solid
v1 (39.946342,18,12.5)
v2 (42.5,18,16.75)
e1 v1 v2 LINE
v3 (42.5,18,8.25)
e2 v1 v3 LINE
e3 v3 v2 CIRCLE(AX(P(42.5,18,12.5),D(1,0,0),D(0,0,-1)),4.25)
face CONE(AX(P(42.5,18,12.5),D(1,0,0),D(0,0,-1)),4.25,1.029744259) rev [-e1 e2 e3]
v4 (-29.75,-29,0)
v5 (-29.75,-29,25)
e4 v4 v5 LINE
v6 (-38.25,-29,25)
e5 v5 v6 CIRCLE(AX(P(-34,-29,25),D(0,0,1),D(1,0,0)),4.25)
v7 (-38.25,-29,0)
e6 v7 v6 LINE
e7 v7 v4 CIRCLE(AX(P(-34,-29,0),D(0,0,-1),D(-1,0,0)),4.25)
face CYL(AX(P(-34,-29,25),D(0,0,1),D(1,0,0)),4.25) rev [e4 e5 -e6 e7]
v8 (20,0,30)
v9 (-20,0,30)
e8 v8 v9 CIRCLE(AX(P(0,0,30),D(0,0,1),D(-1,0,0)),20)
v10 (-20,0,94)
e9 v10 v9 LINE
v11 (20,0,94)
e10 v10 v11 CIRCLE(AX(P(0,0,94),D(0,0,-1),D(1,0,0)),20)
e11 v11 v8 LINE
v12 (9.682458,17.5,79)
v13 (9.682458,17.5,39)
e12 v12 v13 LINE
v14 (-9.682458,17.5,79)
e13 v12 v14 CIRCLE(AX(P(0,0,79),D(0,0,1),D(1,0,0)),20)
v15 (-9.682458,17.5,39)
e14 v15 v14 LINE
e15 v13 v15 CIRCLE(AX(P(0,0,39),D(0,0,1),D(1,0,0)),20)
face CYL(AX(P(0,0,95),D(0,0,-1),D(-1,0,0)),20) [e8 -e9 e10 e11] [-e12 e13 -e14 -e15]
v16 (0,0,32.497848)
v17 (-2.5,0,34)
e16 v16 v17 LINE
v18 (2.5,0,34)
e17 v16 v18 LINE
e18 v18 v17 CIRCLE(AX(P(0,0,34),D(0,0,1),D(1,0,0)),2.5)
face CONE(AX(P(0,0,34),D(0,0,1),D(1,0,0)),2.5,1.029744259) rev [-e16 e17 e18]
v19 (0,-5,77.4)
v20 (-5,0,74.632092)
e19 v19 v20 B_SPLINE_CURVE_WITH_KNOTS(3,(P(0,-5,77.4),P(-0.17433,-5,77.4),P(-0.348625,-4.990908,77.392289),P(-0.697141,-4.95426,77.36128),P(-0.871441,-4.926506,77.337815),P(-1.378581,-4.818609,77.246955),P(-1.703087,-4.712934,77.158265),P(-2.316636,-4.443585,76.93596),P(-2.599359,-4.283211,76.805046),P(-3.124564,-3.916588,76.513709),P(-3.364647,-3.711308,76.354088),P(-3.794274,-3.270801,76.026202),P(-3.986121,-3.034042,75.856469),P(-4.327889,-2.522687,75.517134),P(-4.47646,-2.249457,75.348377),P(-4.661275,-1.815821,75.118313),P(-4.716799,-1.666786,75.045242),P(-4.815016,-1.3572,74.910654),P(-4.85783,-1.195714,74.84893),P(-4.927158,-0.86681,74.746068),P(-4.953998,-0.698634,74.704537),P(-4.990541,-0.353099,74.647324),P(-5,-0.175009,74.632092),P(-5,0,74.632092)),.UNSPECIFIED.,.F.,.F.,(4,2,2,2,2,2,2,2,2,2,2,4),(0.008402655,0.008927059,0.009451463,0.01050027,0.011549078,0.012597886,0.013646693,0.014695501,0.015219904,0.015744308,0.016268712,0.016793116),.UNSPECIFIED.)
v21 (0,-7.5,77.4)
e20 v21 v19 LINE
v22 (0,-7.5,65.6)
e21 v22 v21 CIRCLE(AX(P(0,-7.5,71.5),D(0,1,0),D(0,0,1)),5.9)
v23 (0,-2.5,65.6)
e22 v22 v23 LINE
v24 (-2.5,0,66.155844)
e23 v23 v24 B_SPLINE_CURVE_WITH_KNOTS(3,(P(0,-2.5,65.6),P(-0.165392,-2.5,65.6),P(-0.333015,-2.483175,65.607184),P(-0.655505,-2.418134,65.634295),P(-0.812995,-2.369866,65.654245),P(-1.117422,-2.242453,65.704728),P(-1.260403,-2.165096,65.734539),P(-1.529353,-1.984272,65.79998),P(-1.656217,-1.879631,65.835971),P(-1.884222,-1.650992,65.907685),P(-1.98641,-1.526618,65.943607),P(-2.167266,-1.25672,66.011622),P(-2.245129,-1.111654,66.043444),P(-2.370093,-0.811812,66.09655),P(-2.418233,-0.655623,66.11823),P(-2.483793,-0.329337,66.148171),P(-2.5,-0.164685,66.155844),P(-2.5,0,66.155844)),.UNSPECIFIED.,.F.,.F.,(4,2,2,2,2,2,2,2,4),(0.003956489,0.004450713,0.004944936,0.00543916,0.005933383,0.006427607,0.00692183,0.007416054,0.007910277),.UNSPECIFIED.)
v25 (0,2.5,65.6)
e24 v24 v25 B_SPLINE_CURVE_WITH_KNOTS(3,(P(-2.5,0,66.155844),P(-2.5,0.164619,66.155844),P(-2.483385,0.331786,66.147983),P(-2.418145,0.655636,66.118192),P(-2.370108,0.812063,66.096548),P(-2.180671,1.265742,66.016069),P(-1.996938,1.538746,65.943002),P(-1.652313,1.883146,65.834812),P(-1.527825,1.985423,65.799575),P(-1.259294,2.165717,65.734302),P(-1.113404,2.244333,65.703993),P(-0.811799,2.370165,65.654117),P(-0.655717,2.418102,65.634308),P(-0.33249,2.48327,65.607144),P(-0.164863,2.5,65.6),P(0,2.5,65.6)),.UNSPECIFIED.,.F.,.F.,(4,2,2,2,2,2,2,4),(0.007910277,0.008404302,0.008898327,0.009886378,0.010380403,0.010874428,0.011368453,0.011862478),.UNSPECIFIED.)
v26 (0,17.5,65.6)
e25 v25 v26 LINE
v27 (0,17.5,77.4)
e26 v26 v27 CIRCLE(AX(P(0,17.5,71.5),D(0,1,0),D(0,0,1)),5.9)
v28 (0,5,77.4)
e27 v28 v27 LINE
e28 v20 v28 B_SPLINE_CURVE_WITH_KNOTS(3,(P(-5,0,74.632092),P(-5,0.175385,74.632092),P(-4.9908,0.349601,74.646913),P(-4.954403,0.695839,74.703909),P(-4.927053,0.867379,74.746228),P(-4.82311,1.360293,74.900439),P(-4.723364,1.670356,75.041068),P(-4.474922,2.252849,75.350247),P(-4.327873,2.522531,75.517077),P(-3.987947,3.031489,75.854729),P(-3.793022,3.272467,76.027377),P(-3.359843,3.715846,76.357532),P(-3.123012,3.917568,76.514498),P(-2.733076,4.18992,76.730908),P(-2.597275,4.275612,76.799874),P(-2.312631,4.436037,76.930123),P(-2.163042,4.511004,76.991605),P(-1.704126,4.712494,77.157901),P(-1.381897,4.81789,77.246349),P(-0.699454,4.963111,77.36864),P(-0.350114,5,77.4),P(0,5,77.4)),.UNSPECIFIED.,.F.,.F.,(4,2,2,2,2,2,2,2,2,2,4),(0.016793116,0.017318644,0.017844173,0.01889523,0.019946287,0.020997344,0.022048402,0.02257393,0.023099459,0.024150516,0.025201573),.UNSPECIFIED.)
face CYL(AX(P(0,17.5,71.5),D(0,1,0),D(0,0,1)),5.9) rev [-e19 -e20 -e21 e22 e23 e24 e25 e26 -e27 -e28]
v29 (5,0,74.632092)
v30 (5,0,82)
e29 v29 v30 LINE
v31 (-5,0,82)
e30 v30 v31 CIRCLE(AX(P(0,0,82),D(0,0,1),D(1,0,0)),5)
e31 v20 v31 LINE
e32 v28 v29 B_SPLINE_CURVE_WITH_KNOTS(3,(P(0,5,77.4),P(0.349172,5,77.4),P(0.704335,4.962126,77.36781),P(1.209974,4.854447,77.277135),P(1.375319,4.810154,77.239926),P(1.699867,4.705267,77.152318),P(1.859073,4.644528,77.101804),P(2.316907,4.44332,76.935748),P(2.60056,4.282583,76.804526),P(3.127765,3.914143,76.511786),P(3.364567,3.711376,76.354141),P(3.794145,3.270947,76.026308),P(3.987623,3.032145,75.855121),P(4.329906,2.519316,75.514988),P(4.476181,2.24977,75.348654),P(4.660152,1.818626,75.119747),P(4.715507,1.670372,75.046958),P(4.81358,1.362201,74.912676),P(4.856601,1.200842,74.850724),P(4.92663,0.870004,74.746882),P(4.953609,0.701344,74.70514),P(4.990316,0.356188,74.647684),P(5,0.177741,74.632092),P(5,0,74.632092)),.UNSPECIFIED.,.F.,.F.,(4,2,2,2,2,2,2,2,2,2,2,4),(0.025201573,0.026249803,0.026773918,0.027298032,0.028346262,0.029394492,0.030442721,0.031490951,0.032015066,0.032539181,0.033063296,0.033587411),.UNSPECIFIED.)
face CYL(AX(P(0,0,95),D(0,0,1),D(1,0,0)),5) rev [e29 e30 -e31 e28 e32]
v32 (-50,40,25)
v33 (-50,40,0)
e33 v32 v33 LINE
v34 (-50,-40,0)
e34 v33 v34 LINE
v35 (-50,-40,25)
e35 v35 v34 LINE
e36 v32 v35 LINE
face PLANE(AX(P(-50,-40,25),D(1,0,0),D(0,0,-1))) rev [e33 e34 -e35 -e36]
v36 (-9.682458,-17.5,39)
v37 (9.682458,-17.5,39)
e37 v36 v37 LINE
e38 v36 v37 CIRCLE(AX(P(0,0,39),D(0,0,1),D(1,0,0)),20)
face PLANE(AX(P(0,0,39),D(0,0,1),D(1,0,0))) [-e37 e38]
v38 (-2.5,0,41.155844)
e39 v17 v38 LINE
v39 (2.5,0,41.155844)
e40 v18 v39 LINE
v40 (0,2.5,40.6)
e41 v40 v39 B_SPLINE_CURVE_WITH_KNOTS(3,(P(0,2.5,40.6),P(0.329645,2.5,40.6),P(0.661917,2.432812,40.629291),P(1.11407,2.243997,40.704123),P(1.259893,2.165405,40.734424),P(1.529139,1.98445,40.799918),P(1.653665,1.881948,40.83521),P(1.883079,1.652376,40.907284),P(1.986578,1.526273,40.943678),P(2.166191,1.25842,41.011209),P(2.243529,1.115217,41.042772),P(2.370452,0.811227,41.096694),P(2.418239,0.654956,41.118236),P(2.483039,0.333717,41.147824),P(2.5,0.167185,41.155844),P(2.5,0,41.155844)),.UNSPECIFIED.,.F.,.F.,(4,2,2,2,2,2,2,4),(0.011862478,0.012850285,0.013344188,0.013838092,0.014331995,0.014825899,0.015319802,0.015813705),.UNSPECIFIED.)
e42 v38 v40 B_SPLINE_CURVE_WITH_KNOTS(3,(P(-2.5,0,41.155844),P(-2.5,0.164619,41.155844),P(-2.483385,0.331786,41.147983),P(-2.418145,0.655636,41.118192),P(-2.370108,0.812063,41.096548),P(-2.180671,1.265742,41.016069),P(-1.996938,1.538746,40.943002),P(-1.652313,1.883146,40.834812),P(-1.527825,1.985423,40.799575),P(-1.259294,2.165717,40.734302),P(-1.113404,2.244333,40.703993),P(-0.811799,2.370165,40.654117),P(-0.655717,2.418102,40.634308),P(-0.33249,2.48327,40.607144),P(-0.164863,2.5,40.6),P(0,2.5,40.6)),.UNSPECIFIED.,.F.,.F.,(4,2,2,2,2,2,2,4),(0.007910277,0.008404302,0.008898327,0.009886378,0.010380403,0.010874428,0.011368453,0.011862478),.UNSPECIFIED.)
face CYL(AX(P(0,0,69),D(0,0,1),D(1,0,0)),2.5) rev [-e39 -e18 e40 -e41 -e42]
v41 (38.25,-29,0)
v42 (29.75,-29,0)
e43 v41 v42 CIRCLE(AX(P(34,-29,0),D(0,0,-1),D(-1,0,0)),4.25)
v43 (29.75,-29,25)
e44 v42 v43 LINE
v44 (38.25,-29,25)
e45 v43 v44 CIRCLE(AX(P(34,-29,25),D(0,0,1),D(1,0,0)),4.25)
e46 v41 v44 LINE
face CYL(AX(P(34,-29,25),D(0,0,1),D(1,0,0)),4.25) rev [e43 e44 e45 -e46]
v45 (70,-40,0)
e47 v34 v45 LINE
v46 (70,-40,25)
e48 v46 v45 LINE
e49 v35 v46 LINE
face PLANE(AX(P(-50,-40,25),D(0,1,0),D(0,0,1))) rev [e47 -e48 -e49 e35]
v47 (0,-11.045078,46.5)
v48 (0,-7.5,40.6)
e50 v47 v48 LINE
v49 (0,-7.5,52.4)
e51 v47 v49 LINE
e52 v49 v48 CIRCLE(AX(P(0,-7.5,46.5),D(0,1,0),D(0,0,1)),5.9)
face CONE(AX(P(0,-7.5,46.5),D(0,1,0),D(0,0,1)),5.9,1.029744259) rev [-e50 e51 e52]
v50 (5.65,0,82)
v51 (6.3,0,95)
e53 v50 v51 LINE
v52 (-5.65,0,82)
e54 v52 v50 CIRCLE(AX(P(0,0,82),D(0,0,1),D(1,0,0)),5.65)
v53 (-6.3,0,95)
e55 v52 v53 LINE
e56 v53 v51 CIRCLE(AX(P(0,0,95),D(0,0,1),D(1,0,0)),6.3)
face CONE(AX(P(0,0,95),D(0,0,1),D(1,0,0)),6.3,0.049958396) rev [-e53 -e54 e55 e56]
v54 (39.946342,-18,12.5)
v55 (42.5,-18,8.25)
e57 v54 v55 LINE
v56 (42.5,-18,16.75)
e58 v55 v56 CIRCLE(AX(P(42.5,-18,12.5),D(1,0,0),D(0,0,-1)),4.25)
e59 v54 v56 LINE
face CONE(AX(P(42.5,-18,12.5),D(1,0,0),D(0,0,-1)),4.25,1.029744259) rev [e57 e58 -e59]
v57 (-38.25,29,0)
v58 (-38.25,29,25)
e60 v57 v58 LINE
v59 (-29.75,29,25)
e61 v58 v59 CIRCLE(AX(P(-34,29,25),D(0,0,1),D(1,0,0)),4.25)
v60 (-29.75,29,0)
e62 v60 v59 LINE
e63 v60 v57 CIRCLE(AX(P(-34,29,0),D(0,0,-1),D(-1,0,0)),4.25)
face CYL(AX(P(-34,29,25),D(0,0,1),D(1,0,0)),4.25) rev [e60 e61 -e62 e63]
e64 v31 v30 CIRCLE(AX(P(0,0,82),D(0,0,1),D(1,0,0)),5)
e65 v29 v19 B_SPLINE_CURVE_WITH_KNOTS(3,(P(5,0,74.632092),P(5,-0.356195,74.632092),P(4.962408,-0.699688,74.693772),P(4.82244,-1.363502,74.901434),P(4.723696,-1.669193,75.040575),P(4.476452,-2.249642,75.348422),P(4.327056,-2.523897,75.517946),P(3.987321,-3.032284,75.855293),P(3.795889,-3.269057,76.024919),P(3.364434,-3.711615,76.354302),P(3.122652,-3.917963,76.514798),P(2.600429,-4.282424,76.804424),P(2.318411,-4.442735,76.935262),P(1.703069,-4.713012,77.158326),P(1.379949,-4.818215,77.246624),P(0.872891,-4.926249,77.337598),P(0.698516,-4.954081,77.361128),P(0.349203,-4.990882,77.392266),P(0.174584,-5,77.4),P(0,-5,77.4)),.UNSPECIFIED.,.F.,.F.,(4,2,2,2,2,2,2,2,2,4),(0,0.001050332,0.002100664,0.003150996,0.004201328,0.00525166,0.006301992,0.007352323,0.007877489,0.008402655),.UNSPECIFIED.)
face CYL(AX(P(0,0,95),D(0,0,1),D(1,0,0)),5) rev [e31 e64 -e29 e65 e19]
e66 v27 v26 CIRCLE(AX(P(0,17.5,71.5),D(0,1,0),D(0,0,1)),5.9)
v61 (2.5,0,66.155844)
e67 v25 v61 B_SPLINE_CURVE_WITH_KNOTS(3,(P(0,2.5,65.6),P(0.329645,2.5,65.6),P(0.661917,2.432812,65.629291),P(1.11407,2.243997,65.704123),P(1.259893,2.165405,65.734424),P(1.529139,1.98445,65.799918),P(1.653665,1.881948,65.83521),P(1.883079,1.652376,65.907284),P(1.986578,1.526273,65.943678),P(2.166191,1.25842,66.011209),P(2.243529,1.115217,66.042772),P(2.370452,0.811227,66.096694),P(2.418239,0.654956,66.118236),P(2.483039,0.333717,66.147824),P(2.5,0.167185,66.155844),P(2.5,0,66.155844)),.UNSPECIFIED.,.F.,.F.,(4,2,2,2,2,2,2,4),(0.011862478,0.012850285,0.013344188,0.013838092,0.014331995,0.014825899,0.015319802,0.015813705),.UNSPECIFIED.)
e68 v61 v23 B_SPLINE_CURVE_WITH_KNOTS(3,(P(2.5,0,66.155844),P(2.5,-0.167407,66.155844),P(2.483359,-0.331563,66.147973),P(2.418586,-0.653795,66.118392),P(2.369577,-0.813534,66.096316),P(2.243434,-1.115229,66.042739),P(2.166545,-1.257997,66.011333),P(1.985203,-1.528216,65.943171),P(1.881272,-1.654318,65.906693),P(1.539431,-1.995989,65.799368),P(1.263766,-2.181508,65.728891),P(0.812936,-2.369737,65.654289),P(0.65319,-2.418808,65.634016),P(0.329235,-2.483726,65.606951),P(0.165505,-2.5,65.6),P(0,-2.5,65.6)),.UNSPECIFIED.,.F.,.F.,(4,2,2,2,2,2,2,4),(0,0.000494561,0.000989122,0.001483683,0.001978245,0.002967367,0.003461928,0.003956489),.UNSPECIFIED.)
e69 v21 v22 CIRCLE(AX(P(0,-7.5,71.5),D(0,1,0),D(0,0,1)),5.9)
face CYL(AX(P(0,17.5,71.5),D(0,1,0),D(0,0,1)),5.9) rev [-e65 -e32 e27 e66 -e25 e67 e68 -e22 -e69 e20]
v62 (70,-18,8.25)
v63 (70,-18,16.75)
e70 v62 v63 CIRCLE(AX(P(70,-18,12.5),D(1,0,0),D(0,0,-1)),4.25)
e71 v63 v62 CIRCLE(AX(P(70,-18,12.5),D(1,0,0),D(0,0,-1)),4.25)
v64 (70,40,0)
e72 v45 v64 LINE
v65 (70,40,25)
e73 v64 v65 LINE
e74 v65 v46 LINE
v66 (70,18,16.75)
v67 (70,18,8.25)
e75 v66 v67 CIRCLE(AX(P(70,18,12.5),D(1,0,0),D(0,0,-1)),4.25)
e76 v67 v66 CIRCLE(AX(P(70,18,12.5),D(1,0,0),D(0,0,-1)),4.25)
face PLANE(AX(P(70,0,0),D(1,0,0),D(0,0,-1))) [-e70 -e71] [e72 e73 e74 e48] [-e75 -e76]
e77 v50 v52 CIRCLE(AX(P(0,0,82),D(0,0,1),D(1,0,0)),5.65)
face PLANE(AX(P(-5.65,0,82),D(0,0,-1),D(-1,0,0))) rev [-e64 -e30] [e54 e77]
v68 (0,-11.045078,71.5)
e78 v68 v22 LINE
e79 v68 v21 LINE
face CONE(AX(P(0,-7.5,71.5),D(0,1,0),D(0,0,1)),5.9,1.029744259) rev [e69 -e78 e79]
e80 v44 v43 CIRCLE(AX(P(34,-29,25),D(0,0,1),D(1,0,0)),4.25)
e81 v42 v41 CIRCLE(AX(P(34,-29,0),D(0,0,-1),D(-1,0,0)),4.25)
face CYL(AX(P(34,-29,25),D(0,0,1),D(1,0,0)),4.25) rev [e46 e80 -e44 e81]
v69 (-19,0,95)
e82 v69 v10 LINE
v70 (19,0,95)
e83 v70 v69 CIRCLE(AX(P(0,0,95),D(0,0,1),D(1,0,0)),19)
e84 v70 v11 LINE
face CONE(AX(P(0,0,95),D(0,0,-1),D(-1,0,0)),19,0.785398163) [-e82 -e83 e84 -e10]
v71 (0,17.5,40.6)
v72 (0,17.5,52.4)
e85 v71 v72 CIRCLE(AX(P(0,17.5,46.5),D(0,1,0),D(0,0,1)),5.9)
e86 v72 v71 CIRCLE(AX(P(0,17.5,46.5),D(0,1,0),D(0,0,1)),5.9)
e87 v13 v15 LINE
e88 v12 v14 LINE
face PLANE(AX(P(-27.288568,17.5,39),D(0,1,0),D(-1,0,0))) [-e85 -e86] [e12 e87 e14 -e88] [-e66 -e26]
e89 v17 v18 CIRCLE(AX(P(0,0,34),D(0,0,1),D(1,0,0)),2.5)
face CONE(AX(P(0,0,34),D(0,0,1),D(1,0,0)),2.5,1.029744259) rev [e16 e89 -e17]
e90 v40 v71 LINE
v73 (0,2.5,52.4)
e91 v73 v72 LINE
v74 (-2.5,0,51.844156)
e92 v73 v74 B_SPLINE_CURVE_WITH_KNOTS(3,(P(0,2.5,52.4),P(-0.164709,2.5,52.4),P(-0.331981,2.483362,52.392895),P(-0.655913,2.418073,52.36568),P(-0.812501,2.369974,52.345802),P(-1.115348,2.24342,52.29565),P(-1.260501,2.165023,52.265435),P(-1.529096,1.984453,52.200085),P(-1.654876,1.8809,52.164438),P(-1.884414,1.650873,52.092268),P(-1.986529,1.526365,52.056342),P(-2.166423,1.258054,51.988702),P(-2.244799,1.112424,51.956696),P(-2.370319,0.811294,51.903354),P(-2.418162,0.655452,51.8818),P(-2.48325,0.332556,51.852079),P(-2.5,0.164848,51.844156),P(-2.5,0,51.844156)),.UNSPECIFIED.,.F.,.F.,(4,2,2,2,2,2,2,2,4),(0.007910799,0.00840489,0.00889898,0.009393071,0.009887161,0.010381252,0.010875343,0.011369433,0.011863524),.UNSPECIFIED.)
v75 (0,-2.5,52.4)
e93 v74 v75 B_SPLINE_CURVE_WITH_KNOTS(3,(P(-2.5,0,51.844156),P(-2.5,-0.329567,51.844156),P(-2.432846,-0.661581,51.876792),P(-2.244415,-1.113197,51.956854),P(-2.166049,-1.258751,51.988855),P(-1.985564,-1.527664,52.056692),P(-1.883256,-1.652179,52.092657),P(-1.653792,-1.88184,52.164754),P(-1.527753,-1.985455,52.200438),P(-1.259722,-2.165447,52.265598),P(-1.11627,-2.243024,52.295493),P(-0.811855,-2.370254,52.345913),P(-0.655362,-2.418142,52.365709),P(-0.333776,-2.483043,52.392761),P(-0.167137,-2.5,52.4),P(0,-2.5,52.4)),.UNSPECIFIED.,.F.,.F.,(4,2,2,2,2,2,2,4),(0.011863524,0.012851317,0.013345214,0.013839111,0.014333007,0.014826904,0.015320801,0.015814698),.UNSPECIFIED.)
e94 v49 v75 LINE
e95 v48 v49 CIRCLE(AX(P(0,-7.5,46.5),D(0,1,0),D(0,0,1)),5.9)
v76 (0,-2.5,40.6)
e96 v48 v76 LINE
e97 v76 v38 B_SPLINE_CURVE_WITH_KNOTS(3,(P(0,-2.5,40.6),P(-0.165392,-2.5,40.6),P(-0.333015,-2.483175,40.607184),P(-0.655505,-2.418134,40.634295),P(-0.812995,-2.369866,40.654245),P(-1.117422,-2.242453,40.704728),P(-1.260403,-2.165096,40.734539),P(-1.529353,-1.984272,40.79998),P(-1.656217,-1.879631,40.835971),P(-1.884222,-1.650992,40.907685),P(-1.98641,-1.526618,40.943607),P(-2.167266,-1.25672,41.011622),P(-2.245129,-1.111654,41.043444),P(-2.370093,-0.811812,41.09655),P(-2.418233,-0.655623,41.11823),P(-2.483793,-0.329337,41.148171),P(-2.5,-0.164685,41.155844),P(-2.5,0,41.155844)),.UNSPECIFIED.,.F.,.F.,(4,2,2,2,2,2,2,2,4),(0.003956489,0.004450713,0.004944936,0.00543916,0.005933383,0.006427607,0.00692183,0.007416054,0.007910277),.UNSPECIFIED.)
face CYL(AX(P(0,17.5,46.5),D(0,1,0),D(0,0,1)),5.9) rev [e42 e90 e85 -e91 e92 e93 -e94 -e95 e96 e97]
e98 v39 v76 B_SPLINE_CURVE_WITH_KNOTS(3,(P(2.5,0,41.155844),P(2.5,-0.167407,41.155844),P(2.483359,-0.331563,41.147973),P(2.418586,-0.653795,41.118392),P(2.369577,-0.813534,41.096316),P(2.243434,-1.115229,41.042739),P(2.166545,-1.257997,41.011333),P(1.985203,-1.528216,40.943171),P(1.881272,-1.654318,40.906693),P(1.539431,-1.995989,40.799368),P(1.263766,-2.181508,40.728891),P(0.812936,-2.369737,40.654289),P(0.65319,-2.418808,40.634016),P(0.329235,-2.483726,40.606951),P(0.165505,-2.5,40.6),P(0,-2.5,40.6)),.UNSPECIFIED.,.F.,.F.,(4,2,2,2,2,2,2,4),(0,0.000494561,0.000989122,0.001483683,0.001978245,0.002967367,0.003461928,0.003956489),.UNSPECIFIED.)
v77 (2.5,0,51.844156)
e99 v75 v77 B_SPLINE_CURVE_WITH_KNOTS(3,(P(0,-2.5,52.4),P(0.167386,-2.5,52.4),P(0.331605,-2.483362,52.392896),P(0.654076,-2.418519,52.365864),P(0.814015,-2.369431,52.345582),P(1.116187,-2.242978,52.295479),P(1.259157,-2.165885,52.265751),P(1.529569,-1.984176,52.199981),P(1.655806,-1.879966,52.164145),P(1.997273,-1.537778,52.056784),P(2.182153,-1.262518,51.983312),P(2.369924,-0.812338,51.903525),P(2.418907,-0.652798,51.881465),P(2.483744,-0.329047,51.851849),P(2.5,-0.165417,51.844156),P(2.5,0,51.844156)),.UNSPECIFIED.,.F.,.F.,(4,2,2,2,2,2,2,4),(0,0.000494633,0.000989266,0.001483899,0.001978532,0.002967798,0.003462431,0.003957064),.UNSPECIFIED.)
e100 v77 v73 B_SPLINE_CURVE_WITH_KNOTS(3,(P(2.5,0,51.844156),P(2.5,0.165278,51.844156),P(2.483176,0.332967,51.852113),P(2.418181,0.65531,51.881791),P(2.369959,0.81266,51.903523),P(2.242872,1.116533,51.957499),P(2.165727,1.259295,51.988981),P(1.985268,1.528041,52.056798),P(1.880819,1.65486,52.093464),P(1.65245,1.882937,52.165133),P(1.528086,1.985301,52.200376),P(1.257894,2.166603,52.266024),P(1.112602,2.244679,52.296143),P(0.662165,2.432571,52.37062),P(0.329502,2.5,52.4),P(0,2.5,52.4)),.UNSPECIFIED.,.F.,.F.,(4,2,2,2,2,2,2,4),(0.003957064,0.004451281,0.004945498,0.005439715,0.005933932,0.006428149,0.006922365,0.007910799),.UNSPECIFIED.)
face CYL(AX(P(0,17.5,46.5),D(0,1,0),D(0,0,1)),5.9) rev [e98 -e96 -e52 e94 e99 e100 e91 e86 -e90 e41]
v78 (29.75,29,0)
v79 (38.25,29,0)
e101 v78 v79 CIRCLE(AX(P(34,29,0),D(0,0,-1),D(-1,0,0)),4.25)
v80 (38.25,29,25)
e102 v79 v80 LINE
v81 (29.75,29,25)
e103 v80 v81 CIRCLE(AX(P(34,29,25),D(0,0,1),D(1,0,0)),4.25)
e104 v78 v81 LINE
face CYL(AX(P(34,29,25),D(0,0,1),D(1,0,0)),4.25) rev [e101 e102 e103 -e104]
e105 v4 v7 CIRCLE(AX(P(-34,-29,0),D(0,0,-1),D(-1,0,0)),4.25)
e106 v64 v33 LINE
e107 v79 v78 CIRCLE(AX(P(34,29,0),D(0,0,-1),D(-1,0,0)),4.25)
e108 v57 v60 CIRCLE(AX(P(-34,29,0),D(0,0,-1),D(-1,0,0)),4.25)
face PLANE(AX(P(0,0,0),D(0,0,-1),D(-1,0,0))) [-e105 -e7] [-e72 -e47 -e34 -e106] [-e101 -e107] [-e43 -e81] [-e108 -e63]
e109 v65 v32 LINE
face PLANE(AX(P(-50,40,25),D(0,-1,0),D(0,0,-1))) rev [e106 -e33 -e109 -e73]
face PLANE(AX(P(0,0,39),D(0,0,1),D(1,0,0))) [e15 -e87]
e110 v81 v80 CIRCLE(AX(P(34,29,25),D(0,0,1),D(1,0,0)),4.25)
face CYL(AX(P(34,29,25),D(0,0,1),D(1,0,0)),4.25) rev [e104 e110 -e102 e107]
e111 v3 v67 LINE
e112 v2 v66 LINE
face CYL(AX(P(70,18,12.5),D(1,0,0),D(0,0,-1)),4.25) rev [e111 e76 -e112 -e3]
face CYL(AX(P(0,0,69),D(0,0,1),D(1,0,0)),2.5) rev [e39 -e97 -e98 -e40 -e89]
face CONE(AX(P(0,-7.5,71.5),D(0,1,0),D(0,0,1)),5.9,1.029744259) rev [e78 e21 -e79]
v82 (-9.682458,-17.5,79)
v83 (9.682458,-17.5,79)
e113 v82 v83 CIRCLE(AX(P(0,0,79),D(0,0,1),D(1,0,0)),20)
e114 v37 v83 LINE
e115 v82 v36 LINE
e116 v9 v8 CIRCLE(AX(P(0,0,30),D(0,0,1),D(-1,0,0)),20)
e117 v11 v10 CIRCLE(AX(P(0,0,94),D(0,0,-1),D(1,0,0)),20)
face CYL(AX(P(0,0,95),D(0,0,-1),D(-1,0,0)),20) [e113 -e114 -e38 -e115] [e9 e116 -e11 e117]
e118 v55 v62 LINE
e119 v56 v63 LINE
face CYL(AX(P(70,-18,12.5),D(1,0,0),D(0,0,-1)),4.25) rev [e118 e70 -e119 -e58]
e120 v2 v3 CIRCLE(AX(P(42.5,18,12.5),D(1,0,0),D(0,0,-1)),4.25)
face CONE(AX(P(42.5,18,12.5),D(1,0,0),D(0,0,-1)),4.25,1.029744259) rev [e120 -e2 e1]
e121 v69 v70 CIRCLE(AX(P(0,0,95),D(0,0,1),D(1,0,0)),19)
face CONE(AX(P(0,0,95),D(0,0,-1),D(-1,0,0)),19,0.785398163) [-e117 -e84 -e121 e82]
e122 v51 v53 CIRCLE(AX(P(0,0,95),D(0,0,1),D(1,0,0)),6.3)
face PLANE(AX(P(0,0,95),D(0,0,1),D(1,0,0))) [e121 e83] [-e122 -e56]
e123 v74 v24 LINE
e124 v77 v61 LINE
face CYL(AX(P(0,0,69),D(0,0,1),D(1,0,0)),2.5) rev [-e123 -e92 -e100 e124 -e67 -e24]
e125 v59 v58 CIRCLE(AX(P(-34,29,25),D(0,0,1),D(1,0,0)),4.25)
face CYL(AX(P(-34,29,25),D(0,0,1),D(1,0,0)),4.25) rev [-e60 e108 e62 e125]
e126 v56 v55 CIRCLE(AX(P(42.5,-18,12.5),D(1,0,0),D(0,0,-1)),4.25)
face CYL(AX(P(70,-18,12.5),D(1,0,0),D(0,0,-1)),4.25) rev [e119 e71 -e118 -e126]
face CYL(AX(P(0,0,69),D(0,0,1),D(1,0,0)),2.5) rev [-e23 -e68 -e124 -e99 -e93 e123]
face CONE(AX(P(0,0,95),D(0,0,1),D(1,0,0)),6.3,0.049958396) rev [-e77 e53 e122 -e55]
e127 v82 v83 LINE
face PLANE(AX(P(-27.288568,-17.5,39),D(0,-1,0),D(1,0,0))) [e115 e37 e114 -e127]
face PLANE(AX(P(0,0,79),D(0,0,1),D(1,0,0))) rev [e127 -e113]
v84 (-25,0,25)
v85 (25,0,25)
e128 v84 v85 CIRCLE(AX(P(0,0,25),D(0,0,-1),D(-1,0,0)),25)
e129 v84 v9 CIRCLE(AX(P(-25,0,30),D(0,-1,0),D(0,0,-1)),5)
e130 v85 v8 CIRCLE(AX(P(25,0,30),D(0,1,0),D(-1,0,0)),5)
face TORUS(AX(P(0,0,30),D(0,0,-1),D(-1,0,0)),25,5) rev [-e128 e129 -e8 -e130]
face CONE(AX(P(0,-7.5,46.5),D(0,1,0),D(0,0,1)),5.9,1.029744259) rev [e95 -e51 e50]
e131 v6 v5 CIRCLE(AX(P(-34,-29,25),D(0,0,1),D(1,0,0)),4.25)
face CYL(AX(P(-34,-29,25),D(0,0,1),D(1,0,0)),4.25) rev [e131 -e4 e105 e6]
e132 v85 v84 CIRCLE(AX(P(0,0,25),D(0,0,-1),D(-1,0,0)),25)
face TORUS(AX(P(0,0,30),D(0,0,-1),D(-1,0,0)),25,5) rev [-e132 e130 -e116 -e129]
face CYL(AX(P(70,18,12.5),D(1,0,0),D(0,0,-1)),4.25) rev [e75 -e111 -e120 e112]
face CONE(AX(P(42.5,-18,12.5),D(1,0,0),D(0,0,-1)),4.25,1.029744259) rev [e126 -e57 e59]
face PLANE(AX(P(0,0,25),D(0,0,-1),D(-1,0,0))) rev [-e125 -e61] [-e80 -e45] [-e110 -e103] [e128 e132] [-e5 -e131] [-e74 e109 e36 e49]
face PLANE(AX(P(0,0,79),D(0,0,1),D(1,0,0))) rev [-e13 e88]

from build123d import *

# Parameters (mm, degrees)
SKETCH_13_W                 = 100
SKETCH_13_H                 = 80
EXTRUDE_3_DEPTH             = 25
SKETCH_14_R                 = 0.5
CUT_EXTRUDE_4_DEPTH         = 18
SKETCH_15_R                 = 20
EXTRUDE_4_DEPTH             = 70
HOLE_WIZARD_10_0_10_1_D     = 10
HOLE_WIZARD_10_0_10_1_DEPTH = 25
HOLE_WIZARD_10_0_10_1_TIP   = 3.004303095
SKETCH_21_OUTSIDE_W         = 133.89
SKETCH_21_OUTSIDE_H         = 113.89
SKETCH_21_OUTSIDE_W_2       = 54.577135948
SKETCH_21_OUTSIDE_H_2       = 35
CUT_EXTRUDE_5_DEPTH         = 40
HOLE_WIZARD_G1_4_1_D        = 11.8
HOLE_WIZARD_G1_4_1_DEPTH    = 25
HOLE_WIZARD_G1_4_1_TIP      = 3.545077652
CHAMFER_1_SIZE              = 1
HOLE_WIZARD_M10_1_D         = 8.5
HOLE_WIZARD_M10_1_DEPTH     = 27.5
HOLE_WIZARD_M10_1_TIP       = 2.553657631
FILLET_1_R                  = 5
HOLE_WIZARD_M6_1_D          = 5
HOLE_WIZARD_M6_1_DEPTH      = 35
HOLE_WIZARD_M6_1_TIP        = 1.502151548
SKETCH_35_W                 = 25
SKETCH_35_H                 = 80
EXTRUDE_7_DEPTH             = 20
HOLE_WIZARD_M10_4_D         = 8.5
HOLE_WIZARD_M10_4_DEPTH     = 27.5
HOLE_WIZARD_M10_4_TIP       = 2.553657631


with BuildPart() as part:
    # 草图13 → 凸台-拉伸3 (new body)
    with BuildSketch(Plane.XY):
        Rectangle(SKETCH_13_W, SKETCH_13_H)
    extrude(amount=EXTRUDE_3_DEPTH)

    # 草图14 → 切除-拉伸4 (cut)
    with BuildSketch(Plane.XY.offset(25)):
        with Locations((-34, 29)):
            Circle(SKETCH_14_R)
        with Locations((34, 29)):
            Circle(SKETCH_14_R)
        with Locations((34, -29)):
            Circle(SKETCH_14_R)
        with Locations((-34, -29)):
            Circle(SKETCH_14_R)
    extrude(amount=-CUT_EXTRUDE_4_DEPTH, mode=Mode.SUBTRACT)

    # 草图15 → 凸台-拉伸4 (add)
    with BuildSketch(Plane.XY.offset(25)):
        with Locations(Location((0, 0, 0), (0, 0, 180))):
            Circle(SKETCH_15_R)
    extrude(amount=EXTRUDE_4_DEPTH)

    # Ø10.0 (10) 直径孔1
    with Locations(Plane.XY.offset(95)):
        with Locations((0, 0)):
            Hole(HOLE_WIZARD_10_0_10_1_D / 2, depth=HOLE_WIZARD_10_0_10_1_DEPTH)
            with Locations((0, 0, -(HOLE_WIZARD_10_0_10_1_DEPTH + HOLE_WIZARD_10_0_10_1_TIP / 2))):  # 118° drill point
                Cone(0, HOLE_WIZARD_10_0_10_1_D / 2, HOLE_WIZARD_10_0_10_1_TIP, mode=Mode.SUBTRACT)

    # 草图19 → 切除-旋转10 (revolve, cut)
    with BuildSketch(Plane(origin=(0, 0, 0), x_dir=(1, 0, 0), z_dir=(0, 1, 0)), mode=Mode.PRIVATE) as cut_revolve_10_sk:
        Polygon((-6.3, -95), (-5.65, -82), (-5, -82), (-5, -95), align=None)
    revolve(cut_revolve_10_sk.sketch.rotate(Axis((0, 0, 95), (0, 0, -1)), 180), axis=Axis((0, 0, 95), (0, 0, -1)), mode=Mode.SUBTRACT)

    # 草图21 outside → 切除-拉伸5 (cut)
    with BuildSketch(Plane.XY.offset(79)):
        Rectangle(SKETCH_21_OUTSIDE_W, SKETCH_21_OUTSIDE_H)
        Rectangle(SKETCH_21_OUTSIDE_W_2, SKETCH_21_OUTSIDE_H_2, mode=Mode.SUBTRACT)
    extrude(amount=-CUT_EXTRUDE_5_DEPTH, mode=Mode.SUBTRACT)

    # G1/4 螺纹孔1
    with Locations(Plane(origin=(0, 17.5, 0), x_dir=(1, 0, 0), z_dir=(0, 1, 0))):
        with Locations((0, -71.5), (0, -46.5)):
            Hole(HOLE_WIZARD_G1_4_1_D / 2, depth=HOLE_WIZARD_G1_4_1_DEPTH)
            with Locations((0, 0, -(HOLE_WIZARD_G1_4_1_DEPTH + HOLE_WIZARD_G1_4_1_TIP / 2))):  # 118° drill point
                Cone(0, HOLE_WIZARD_G1_4_1_D / 2, HOLE_WIZARD_G1_4_1_TIP, mode=Mode.SUBTRACT)

    # 倒角1
    chamfer_1_edges = [part.edges().sort_by_distance(p)[0] for p in [
        (20, 0, 95),
    ]]
    chamfer(chamfer_1_edges, length=CHAMFER_1_SIZE)

    # M10 螺纹孔1
    with Locations(Plane.XY.offset(25)):
        with Locations((-34, 29), (34, 29), (34, -29), (-34, -29)):
            Hole(HOLE_WIZARD_M10_1_D / 2, depth=HOLE_WIZARD_M10_1_DEPTH)
            with Locations((0, 0, -(HOLE_WIZARD_M10_1_DEPTH + HOLE_WIZARD_M10_1_TIP / 2))):  # 118° drill point
                Cone(0, HOLE_WIZARD_M10_1_D / 2, HOLE_WIZARD_M10_1_TIP, mode=Mode.SUBTRACT)

    # 圆角1
    fillet_1_edges = [part.edges().sort_by_distance(p)[0] for p in [
        (20, 0, 25),
    ]]
    fillet(fillet_1_edges, radius=FILLET_1_R)

    # M6 螺纹孔1
    with Locations(Plane.XY.offset(69)):
        with Locations((0, 0)):
            Hole(HOLE_WIZARD_M6_1_D / 2, depth=HOLE_WIZARD_M6_1_DEPTH)
            with Locations((0, 0, -(HOLE_WIZARD_M6_1_DEPTH + HOLE_WIZARD_M6_1_TIP / 2))):  # 118° drill point
                Cone(0, HOLE_WIZARD_M6_1_D / 2, HOLE_WIZARD_M6_1_TIP, mode=Mode.SUBTRACT)

    # 草图35 → 凸台-拉伸7 (add)
    with BuildSketch(Plane(origin=(50, 0, 0), x_dir=(0, 0, -1), z_dir=(1, 0, 0))):
        with Locations((-12.5, 0)):
            Rectangle(SKETCH_35_W, SKETCH_35_H)
    extrude(amount=EXTRUDE_7_DEPTH)

    # M10 螺纹孔4
    with Locations(Plane(origin=(70, 0, 0), x_dir=(0, 0, -1), z_dir=(1, 0, 0))):
        with Locations((-12.5, 18), (-12.5, -18)):
            Hole(HOLE_WIZARD_M10_4_D / 2, depth=HOLE_WIZARD_M10_4_DEPTH)
            with Locations((0, 0, -(HOLE_WIZARD_M10_4_DEPTH + HOLE_WIZARD_M10_4_TIP / 2))):  # 118° drill point
                Cone(0, HOLE_WIZARD_M10_4_D / 2, HOLE_WIZARD_M10_4_TIP, mode=Mode.SUBTRACT)


solid = part.part
